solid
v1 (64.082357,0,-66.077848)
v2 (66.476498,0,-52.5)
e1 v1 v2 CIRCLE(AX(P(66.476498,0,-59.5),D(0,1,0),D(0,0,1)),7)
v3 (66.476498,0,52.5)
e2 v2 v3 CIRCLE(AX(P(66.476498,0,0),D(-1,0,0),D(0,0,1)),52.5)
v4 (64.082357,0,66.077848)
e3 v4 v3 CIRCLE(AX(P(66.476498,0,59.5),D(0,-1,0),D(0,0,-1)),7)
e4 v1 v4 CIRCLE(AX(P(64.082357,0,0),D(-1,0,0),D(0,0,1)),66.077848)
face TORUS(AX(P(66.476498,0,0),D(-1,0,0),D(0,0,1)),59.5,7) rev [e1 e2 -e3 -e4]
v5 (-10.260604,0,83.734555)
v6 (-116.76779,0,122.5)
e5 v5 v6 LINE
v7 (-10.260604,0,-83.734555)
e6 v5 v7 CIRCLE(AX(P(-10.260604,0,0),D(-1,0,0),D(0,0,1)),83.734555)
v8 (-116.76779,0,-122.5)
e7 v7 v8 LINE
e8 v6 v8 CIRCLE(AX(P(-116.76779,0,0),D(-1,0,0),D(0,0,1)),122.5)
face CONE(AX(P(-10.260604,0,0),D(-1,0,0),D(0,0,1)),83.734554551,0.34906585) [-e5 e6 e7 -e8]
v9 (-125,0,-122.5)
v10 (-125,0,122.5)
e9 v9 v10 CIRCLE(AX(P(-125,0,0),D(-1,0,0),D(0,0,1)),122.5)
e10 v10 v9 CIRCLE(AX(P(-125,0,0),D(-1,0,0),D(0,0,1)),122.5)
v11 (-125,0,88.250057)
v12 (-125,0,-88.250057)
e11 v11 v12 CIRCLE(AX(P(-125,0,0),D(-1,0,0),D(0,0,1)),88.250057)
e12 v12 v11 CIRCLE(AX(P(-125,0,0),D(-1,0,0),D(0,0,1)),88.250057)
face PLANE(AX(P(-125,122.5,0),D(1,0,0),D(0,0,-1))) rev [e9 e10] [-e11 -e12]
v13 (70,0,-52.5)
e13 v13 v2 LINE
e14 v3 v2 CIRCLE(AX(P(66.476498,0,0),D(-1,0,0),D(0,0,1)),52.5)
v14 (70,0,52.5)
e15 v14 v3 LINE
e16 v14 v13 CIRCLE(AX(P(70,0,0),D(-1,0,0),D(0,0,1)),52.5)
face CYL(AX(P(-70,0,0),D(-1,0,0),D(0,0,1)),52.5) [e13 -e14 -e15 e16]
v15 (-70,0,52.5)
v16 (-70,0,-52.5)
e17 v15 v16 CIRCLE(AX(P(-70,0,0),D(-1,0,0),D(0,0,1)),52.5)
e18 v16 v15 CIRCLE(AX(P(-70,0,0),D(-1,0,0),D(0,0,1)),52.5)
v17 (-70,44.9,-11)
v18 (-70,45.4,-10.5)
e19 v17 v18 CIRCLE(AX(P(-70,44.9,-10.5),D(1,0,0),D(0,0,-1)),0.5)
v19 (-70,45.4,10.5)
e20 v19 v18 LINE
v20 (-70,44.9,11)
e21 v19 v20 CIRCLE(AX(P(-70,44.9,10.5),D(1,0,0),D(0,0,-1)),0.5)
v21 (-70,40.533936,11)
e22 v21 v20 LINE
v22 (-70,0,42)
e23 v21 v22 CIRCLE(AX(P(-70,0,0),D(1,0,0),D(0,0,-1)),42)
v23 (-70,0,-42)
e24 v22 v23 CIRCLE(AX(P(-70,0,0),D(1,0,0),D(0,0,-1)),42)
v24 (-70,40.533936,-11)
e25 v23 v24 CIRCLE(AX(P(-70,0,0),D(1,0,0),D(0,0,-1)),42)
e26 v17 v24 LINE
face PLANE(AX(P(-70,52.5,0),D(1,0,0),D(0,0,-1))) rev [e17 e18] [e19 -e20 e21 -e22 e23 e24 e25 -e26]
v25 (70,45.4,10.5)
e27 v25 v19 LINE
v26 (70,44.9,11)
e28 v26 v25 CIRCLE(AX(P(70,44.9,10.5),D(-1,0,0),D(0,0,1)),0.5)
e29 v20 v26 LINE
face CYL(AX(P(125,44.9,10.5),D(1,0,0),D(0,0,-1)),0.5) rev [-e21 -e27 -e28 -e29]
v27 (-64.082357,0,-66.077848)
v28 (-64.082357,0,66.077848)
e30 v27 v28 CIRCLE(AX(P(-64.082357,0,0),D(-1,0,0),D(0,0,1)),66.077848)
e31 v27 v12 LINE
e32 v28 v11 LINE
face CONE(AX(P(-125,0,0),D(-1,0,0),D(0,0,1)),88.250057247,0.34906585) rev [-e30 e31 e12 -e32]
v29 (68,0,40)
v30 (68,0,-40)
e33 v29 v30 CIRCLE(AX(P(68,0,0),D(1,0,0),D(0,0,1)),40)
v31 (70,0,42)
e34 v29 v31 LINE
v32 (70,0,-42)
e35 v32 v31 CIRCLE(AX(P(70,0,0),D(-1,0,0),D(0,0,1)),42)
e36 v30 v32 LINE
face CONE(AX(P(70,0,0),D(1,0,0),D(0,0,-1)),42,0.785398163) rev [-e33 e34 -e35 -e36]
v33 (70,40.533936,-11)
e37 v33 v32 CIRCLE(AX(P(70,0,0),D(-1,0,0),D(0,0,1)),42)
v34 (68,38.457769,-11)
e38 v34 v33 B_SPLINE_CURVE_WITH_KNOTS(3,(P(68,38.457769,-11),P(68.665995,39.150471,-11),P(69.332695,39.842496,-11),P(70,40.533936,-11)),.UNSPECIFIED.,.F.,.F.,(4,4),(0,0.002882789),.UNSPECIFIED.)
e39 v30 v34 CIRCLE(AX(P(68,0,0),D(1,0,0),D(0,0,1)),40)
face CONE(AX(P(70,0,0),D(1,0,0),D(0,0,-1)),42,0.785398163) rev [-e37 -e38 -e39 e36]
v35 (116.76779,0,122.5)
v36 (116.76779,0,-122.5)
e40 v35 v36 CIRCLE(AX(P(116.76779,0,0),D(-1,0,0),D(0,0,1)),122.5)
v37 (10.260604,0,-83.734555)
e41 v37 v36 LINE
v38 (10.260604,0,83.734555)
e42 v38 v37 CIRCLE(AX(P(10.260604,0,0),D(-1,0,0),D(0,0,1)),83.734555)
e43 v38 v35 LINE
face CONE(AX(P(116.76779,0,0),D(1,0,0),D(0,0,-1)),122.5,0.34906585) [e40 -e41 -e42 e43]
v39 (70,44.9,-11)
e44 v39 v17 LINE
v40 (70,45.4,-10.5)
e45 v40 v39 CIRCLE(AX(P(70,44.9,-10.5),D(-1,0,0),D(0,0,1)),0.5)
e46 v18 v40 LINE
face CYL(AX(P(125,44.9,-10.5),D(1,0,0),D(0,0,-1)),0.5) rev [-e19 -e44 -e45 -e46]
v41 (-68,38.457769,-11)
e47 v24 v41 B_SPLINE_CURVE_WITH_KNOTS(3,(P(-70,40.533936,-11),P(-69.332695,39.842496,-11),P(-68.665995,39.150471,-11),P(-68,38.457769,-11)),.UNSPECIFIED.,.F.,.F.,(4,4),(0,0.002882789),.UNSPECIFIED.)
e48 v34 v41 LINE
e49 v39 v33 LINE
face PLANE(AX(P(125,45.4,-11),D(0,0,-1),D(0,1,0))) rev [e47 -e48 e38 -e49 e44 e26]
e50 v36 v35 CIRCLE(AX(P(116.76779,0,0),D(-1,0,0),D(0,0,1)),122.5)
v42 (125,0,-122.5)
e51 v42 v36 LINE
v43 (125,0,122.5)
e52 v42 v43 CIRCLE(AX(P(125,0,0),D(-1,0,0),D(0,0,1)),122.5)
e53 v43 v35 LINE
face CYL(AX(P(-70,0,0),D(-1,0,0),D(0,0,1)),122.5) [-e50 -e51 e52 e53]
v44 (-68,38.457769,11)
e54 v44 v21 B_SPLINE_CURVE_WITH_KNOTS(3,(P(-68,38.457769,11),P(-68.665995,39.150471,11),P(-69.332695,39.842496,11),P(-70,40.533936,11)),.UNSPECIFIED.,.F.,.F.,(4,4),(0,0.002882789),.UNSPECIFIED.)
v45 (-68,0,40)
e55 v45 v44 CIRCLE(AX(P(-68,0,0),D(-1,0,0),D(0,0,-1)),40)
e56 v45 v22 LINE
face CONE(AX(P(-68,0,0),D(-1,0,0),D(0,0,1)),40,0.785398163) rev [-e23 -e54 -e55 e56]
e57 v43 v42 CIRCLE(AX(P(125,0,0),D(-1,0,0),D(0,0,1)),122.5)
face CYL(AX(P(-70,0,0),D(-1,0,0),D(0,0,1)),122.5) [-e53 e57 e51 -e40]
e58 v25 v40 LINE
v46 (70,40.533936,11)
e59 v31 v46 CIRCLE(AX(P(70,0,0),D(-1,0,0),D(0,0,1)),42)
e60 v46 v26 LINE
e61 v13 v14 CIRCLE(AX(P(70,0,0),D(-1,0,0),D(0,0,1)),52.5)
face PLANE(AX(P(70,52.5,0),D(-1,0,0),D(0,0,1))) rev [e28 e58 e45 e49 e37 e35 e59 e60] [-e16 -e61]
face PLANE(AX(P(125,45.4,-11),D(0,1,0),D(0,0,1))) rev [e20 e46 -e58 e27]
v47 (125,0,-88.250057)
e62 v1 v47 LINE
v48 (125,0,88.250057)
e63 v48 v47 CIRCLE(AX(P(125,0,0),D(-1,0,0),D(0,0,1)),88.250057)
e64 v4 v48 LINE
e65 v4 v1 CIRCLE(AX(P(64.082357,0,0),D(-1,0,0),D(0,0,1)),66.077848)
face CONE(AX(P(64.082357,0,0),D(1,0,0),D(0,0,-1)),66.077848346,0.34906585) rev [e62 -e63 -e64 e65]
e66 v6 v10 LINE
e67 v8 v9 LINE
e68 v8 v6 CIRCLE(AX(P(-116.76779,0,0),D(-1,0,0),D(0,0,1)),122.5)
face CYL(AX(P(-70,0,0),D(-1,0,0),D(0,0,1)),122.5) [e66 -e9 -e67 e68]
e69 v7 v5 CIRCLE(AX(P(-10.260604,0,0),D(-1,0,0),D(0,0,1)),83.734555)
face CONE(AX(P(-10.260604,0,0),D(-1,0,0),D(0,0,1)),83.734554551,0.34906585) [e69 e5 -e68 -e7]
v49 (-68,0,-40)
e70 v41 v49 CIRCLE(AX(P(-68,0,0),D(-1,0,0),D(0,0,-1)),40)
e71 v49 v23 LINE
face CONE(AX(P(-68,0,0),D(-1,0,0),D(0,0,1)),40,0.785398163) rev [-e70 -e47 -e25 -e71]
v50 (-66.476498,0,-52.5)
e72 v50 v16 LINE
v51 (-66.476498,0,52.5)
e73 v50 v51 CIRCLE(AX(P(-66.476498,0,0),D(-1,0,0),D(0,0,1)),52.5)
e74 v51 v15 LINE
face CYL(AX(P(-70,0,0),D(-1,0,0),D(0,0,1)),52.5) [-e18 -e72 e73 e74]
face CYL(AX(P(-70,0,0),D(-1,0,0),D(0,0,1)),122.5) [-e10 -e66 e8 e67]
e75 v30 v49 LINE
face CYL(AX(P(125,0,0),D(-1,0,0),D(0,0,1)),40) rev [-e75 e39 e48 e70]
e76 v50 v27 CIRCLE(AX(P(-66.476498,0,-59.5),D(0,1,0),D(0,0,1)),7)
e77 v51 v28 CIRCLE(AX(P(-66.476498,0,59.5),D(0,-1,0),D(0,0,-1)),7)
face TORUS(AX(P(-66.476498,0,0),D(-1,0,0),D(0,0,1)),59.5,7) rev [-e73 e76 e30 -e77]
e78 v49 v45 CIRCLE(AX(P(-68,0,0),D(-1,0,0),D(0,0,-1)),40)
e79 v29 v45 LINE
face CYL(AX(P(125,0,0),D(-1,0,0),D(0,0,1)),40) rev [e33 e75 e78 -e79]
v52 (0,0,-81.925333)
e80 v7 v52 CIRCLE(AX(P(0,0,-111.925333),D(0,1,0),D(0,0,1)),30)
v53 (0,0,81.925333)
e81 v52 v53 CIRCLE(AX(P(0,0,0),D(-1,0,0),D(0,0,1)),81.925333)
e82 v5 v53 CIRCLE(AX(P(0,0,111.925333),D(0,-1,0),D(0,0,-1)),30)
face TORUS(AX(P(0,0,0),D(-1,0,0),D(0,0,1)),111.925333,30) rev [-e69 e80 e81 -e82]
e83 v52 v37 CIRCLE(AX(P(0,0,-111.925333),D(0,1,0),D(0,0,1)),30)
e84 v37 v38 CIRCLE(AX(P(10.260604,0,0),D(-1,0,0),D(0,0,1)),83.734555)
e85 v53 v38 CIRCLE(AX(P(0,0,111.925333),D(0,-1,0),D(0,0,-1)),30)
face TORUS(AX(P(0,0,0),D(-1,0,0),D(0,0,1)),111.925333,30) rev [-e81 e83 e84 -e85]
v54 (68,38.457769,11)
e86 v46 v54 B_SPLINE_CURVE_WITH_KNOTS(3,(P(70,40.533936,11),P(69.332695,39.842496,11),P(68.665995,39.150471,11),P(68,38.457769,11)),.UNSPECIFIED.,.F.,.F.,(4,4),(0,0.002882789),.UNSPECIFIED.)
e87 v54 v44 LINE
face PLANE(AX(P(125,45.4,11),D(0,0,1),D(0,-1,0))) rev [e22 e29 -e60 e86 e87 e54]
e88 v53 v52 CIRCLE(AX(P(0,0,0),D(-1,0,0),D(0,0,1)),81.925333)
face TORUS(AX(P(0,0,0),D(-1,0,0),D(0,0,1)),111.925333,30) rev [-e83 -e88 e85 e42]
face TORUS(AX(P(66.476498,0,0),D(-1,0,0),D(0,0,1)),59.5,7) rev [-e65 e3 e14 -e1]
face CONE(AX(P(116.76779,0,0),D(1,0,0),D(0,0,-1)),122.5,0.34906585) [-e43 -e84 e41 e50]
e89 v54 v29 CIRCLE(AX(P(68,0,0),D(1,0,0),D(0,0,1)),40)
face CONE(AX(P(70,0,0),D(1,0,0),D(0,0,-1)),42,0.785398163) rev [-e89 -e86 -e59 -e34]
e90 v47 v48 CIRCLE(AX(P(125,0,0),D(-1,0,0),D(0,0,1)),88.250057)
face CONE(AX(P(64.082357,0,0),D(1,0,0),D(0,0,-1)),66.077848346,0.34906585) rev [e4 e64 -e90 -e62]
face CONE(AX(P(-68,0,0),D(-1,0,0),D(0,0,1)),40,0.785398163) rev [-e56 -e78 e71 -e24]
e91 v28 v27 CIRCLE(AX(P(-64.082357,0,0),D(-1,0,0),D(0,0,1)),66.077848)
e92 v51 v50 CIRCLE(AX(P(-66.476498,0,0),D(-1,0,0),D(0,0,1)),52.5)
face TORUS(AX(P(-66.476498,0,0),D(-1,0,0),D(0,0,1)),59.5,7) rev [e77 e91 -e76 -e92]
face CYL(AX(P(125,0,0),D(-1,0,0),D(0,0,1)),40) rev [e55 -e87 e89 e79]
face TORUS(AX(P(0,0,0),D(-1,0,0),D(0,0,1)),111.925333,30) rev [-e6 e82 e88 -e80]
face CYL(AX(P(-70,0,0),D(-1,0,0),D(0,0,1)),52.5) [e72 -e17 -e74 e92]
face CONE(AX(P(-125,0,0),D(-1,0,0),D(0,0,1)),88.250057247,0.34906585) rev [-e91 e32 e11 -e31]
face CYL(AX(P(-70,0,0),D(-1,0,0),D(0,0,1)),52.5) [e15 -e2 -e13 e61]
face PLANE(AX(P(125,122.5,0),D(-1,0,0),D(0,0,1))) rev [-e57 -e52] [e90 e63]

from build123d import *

# Parameters (mm, degrees)
CUT_EXTRUDE1_DEPTH = 261.839989265
CHAMFER1_SIZE      = 2
FILLET1_R          = 0.5


with BuildPart() as part:
    # Sketch1 → Revolve1 (revolve)
    with BuildSketch(Plane.XY, mode=Mode.PRIVATE) as revolve1_sk:
        with BuildLine():
            Line((-125, 122.5), (-116.767790327, 122.5))
            Line((-116.767790327, 122.5), (-10.2606043, 83.734554551))
            ThreePointArc((-10.2606043, 83.734554551), (0, 81.925333174), (10.2606043, 83.734554551))
            Line((10.2606043, 83.734554551), (116.767790327, 122.5))
            Line((116.767790327, 122.5), (125, 122.5))
            Line((125, 122.5), (125, 88.250057247))
            Line((125, 88.250057247), (64.082356705, 66.077848346))
            ThreePointArc((64.082356705, 66.077848346), (59.582843437, 58.284462756), (66.476497708, 52.5))
            Line((66.476497708, 52.5), (70, 52.5))
            Line((70, 52.5), (70, 0))
            Line((70, 0), (-70, 0))
            Line((-70, 0), (-70, 52.5))
            Line((-70, 52.5), (-66.476497708, 52.5))
            ThreePointArc((-66.476497708, 52.5), (-59.582843437, 58.284462756), (-64.082356705, 66.077848346))
            Line((-64.082356705, 66.077848346), (-125, 88.250057247))
            Line((-125, 88.250057247), (-125, 122.5))
        make_face()
    revolve(revolve1_sk.sketch.rotate(Axis((-70, 0, 0), (1, 0, 0)), 90), axis=Axis((-70, 0, 0), (1, 0, 0)))

    # Sketch2 → Cut-Extrude1 (cut, through all)
    with BuildSketch(Plane.ZY.offset(70)):
        with BuildLine():
            Line((-11, 45.4), (11, 45.4))
            Line((11, 45.4), (11, 38.457769046))
            ThreePointArc((11, 38.457769046), (0, -40), (-11, 38.457769046))
            Line((-11, 38.457769046), (-11, 45.4))
        make_face()
    extrude(amount=-CUT_EXTRUDE1_DEPTH, mode=Mode.SUBTRACT)

    # Chamfer1
    chamfer1_edges = [part.edges().sort_by_distance(p)[0] for p in [
        (70, -40, 0),
        (-70, -40, 0),
    ]]
    chamfer(chamfer1_edges, length=CHAMFER1_SIZE)

    # Fillet1
    fillet1_edges = [part.edges().sort_by_distance(p)[0] for p in [
        (0, 45.4, -11),
        (0, 45.4, 11),
    ]]
    fillet(fillet1_edges, radius=FILLET1_R)


solid = part.part
